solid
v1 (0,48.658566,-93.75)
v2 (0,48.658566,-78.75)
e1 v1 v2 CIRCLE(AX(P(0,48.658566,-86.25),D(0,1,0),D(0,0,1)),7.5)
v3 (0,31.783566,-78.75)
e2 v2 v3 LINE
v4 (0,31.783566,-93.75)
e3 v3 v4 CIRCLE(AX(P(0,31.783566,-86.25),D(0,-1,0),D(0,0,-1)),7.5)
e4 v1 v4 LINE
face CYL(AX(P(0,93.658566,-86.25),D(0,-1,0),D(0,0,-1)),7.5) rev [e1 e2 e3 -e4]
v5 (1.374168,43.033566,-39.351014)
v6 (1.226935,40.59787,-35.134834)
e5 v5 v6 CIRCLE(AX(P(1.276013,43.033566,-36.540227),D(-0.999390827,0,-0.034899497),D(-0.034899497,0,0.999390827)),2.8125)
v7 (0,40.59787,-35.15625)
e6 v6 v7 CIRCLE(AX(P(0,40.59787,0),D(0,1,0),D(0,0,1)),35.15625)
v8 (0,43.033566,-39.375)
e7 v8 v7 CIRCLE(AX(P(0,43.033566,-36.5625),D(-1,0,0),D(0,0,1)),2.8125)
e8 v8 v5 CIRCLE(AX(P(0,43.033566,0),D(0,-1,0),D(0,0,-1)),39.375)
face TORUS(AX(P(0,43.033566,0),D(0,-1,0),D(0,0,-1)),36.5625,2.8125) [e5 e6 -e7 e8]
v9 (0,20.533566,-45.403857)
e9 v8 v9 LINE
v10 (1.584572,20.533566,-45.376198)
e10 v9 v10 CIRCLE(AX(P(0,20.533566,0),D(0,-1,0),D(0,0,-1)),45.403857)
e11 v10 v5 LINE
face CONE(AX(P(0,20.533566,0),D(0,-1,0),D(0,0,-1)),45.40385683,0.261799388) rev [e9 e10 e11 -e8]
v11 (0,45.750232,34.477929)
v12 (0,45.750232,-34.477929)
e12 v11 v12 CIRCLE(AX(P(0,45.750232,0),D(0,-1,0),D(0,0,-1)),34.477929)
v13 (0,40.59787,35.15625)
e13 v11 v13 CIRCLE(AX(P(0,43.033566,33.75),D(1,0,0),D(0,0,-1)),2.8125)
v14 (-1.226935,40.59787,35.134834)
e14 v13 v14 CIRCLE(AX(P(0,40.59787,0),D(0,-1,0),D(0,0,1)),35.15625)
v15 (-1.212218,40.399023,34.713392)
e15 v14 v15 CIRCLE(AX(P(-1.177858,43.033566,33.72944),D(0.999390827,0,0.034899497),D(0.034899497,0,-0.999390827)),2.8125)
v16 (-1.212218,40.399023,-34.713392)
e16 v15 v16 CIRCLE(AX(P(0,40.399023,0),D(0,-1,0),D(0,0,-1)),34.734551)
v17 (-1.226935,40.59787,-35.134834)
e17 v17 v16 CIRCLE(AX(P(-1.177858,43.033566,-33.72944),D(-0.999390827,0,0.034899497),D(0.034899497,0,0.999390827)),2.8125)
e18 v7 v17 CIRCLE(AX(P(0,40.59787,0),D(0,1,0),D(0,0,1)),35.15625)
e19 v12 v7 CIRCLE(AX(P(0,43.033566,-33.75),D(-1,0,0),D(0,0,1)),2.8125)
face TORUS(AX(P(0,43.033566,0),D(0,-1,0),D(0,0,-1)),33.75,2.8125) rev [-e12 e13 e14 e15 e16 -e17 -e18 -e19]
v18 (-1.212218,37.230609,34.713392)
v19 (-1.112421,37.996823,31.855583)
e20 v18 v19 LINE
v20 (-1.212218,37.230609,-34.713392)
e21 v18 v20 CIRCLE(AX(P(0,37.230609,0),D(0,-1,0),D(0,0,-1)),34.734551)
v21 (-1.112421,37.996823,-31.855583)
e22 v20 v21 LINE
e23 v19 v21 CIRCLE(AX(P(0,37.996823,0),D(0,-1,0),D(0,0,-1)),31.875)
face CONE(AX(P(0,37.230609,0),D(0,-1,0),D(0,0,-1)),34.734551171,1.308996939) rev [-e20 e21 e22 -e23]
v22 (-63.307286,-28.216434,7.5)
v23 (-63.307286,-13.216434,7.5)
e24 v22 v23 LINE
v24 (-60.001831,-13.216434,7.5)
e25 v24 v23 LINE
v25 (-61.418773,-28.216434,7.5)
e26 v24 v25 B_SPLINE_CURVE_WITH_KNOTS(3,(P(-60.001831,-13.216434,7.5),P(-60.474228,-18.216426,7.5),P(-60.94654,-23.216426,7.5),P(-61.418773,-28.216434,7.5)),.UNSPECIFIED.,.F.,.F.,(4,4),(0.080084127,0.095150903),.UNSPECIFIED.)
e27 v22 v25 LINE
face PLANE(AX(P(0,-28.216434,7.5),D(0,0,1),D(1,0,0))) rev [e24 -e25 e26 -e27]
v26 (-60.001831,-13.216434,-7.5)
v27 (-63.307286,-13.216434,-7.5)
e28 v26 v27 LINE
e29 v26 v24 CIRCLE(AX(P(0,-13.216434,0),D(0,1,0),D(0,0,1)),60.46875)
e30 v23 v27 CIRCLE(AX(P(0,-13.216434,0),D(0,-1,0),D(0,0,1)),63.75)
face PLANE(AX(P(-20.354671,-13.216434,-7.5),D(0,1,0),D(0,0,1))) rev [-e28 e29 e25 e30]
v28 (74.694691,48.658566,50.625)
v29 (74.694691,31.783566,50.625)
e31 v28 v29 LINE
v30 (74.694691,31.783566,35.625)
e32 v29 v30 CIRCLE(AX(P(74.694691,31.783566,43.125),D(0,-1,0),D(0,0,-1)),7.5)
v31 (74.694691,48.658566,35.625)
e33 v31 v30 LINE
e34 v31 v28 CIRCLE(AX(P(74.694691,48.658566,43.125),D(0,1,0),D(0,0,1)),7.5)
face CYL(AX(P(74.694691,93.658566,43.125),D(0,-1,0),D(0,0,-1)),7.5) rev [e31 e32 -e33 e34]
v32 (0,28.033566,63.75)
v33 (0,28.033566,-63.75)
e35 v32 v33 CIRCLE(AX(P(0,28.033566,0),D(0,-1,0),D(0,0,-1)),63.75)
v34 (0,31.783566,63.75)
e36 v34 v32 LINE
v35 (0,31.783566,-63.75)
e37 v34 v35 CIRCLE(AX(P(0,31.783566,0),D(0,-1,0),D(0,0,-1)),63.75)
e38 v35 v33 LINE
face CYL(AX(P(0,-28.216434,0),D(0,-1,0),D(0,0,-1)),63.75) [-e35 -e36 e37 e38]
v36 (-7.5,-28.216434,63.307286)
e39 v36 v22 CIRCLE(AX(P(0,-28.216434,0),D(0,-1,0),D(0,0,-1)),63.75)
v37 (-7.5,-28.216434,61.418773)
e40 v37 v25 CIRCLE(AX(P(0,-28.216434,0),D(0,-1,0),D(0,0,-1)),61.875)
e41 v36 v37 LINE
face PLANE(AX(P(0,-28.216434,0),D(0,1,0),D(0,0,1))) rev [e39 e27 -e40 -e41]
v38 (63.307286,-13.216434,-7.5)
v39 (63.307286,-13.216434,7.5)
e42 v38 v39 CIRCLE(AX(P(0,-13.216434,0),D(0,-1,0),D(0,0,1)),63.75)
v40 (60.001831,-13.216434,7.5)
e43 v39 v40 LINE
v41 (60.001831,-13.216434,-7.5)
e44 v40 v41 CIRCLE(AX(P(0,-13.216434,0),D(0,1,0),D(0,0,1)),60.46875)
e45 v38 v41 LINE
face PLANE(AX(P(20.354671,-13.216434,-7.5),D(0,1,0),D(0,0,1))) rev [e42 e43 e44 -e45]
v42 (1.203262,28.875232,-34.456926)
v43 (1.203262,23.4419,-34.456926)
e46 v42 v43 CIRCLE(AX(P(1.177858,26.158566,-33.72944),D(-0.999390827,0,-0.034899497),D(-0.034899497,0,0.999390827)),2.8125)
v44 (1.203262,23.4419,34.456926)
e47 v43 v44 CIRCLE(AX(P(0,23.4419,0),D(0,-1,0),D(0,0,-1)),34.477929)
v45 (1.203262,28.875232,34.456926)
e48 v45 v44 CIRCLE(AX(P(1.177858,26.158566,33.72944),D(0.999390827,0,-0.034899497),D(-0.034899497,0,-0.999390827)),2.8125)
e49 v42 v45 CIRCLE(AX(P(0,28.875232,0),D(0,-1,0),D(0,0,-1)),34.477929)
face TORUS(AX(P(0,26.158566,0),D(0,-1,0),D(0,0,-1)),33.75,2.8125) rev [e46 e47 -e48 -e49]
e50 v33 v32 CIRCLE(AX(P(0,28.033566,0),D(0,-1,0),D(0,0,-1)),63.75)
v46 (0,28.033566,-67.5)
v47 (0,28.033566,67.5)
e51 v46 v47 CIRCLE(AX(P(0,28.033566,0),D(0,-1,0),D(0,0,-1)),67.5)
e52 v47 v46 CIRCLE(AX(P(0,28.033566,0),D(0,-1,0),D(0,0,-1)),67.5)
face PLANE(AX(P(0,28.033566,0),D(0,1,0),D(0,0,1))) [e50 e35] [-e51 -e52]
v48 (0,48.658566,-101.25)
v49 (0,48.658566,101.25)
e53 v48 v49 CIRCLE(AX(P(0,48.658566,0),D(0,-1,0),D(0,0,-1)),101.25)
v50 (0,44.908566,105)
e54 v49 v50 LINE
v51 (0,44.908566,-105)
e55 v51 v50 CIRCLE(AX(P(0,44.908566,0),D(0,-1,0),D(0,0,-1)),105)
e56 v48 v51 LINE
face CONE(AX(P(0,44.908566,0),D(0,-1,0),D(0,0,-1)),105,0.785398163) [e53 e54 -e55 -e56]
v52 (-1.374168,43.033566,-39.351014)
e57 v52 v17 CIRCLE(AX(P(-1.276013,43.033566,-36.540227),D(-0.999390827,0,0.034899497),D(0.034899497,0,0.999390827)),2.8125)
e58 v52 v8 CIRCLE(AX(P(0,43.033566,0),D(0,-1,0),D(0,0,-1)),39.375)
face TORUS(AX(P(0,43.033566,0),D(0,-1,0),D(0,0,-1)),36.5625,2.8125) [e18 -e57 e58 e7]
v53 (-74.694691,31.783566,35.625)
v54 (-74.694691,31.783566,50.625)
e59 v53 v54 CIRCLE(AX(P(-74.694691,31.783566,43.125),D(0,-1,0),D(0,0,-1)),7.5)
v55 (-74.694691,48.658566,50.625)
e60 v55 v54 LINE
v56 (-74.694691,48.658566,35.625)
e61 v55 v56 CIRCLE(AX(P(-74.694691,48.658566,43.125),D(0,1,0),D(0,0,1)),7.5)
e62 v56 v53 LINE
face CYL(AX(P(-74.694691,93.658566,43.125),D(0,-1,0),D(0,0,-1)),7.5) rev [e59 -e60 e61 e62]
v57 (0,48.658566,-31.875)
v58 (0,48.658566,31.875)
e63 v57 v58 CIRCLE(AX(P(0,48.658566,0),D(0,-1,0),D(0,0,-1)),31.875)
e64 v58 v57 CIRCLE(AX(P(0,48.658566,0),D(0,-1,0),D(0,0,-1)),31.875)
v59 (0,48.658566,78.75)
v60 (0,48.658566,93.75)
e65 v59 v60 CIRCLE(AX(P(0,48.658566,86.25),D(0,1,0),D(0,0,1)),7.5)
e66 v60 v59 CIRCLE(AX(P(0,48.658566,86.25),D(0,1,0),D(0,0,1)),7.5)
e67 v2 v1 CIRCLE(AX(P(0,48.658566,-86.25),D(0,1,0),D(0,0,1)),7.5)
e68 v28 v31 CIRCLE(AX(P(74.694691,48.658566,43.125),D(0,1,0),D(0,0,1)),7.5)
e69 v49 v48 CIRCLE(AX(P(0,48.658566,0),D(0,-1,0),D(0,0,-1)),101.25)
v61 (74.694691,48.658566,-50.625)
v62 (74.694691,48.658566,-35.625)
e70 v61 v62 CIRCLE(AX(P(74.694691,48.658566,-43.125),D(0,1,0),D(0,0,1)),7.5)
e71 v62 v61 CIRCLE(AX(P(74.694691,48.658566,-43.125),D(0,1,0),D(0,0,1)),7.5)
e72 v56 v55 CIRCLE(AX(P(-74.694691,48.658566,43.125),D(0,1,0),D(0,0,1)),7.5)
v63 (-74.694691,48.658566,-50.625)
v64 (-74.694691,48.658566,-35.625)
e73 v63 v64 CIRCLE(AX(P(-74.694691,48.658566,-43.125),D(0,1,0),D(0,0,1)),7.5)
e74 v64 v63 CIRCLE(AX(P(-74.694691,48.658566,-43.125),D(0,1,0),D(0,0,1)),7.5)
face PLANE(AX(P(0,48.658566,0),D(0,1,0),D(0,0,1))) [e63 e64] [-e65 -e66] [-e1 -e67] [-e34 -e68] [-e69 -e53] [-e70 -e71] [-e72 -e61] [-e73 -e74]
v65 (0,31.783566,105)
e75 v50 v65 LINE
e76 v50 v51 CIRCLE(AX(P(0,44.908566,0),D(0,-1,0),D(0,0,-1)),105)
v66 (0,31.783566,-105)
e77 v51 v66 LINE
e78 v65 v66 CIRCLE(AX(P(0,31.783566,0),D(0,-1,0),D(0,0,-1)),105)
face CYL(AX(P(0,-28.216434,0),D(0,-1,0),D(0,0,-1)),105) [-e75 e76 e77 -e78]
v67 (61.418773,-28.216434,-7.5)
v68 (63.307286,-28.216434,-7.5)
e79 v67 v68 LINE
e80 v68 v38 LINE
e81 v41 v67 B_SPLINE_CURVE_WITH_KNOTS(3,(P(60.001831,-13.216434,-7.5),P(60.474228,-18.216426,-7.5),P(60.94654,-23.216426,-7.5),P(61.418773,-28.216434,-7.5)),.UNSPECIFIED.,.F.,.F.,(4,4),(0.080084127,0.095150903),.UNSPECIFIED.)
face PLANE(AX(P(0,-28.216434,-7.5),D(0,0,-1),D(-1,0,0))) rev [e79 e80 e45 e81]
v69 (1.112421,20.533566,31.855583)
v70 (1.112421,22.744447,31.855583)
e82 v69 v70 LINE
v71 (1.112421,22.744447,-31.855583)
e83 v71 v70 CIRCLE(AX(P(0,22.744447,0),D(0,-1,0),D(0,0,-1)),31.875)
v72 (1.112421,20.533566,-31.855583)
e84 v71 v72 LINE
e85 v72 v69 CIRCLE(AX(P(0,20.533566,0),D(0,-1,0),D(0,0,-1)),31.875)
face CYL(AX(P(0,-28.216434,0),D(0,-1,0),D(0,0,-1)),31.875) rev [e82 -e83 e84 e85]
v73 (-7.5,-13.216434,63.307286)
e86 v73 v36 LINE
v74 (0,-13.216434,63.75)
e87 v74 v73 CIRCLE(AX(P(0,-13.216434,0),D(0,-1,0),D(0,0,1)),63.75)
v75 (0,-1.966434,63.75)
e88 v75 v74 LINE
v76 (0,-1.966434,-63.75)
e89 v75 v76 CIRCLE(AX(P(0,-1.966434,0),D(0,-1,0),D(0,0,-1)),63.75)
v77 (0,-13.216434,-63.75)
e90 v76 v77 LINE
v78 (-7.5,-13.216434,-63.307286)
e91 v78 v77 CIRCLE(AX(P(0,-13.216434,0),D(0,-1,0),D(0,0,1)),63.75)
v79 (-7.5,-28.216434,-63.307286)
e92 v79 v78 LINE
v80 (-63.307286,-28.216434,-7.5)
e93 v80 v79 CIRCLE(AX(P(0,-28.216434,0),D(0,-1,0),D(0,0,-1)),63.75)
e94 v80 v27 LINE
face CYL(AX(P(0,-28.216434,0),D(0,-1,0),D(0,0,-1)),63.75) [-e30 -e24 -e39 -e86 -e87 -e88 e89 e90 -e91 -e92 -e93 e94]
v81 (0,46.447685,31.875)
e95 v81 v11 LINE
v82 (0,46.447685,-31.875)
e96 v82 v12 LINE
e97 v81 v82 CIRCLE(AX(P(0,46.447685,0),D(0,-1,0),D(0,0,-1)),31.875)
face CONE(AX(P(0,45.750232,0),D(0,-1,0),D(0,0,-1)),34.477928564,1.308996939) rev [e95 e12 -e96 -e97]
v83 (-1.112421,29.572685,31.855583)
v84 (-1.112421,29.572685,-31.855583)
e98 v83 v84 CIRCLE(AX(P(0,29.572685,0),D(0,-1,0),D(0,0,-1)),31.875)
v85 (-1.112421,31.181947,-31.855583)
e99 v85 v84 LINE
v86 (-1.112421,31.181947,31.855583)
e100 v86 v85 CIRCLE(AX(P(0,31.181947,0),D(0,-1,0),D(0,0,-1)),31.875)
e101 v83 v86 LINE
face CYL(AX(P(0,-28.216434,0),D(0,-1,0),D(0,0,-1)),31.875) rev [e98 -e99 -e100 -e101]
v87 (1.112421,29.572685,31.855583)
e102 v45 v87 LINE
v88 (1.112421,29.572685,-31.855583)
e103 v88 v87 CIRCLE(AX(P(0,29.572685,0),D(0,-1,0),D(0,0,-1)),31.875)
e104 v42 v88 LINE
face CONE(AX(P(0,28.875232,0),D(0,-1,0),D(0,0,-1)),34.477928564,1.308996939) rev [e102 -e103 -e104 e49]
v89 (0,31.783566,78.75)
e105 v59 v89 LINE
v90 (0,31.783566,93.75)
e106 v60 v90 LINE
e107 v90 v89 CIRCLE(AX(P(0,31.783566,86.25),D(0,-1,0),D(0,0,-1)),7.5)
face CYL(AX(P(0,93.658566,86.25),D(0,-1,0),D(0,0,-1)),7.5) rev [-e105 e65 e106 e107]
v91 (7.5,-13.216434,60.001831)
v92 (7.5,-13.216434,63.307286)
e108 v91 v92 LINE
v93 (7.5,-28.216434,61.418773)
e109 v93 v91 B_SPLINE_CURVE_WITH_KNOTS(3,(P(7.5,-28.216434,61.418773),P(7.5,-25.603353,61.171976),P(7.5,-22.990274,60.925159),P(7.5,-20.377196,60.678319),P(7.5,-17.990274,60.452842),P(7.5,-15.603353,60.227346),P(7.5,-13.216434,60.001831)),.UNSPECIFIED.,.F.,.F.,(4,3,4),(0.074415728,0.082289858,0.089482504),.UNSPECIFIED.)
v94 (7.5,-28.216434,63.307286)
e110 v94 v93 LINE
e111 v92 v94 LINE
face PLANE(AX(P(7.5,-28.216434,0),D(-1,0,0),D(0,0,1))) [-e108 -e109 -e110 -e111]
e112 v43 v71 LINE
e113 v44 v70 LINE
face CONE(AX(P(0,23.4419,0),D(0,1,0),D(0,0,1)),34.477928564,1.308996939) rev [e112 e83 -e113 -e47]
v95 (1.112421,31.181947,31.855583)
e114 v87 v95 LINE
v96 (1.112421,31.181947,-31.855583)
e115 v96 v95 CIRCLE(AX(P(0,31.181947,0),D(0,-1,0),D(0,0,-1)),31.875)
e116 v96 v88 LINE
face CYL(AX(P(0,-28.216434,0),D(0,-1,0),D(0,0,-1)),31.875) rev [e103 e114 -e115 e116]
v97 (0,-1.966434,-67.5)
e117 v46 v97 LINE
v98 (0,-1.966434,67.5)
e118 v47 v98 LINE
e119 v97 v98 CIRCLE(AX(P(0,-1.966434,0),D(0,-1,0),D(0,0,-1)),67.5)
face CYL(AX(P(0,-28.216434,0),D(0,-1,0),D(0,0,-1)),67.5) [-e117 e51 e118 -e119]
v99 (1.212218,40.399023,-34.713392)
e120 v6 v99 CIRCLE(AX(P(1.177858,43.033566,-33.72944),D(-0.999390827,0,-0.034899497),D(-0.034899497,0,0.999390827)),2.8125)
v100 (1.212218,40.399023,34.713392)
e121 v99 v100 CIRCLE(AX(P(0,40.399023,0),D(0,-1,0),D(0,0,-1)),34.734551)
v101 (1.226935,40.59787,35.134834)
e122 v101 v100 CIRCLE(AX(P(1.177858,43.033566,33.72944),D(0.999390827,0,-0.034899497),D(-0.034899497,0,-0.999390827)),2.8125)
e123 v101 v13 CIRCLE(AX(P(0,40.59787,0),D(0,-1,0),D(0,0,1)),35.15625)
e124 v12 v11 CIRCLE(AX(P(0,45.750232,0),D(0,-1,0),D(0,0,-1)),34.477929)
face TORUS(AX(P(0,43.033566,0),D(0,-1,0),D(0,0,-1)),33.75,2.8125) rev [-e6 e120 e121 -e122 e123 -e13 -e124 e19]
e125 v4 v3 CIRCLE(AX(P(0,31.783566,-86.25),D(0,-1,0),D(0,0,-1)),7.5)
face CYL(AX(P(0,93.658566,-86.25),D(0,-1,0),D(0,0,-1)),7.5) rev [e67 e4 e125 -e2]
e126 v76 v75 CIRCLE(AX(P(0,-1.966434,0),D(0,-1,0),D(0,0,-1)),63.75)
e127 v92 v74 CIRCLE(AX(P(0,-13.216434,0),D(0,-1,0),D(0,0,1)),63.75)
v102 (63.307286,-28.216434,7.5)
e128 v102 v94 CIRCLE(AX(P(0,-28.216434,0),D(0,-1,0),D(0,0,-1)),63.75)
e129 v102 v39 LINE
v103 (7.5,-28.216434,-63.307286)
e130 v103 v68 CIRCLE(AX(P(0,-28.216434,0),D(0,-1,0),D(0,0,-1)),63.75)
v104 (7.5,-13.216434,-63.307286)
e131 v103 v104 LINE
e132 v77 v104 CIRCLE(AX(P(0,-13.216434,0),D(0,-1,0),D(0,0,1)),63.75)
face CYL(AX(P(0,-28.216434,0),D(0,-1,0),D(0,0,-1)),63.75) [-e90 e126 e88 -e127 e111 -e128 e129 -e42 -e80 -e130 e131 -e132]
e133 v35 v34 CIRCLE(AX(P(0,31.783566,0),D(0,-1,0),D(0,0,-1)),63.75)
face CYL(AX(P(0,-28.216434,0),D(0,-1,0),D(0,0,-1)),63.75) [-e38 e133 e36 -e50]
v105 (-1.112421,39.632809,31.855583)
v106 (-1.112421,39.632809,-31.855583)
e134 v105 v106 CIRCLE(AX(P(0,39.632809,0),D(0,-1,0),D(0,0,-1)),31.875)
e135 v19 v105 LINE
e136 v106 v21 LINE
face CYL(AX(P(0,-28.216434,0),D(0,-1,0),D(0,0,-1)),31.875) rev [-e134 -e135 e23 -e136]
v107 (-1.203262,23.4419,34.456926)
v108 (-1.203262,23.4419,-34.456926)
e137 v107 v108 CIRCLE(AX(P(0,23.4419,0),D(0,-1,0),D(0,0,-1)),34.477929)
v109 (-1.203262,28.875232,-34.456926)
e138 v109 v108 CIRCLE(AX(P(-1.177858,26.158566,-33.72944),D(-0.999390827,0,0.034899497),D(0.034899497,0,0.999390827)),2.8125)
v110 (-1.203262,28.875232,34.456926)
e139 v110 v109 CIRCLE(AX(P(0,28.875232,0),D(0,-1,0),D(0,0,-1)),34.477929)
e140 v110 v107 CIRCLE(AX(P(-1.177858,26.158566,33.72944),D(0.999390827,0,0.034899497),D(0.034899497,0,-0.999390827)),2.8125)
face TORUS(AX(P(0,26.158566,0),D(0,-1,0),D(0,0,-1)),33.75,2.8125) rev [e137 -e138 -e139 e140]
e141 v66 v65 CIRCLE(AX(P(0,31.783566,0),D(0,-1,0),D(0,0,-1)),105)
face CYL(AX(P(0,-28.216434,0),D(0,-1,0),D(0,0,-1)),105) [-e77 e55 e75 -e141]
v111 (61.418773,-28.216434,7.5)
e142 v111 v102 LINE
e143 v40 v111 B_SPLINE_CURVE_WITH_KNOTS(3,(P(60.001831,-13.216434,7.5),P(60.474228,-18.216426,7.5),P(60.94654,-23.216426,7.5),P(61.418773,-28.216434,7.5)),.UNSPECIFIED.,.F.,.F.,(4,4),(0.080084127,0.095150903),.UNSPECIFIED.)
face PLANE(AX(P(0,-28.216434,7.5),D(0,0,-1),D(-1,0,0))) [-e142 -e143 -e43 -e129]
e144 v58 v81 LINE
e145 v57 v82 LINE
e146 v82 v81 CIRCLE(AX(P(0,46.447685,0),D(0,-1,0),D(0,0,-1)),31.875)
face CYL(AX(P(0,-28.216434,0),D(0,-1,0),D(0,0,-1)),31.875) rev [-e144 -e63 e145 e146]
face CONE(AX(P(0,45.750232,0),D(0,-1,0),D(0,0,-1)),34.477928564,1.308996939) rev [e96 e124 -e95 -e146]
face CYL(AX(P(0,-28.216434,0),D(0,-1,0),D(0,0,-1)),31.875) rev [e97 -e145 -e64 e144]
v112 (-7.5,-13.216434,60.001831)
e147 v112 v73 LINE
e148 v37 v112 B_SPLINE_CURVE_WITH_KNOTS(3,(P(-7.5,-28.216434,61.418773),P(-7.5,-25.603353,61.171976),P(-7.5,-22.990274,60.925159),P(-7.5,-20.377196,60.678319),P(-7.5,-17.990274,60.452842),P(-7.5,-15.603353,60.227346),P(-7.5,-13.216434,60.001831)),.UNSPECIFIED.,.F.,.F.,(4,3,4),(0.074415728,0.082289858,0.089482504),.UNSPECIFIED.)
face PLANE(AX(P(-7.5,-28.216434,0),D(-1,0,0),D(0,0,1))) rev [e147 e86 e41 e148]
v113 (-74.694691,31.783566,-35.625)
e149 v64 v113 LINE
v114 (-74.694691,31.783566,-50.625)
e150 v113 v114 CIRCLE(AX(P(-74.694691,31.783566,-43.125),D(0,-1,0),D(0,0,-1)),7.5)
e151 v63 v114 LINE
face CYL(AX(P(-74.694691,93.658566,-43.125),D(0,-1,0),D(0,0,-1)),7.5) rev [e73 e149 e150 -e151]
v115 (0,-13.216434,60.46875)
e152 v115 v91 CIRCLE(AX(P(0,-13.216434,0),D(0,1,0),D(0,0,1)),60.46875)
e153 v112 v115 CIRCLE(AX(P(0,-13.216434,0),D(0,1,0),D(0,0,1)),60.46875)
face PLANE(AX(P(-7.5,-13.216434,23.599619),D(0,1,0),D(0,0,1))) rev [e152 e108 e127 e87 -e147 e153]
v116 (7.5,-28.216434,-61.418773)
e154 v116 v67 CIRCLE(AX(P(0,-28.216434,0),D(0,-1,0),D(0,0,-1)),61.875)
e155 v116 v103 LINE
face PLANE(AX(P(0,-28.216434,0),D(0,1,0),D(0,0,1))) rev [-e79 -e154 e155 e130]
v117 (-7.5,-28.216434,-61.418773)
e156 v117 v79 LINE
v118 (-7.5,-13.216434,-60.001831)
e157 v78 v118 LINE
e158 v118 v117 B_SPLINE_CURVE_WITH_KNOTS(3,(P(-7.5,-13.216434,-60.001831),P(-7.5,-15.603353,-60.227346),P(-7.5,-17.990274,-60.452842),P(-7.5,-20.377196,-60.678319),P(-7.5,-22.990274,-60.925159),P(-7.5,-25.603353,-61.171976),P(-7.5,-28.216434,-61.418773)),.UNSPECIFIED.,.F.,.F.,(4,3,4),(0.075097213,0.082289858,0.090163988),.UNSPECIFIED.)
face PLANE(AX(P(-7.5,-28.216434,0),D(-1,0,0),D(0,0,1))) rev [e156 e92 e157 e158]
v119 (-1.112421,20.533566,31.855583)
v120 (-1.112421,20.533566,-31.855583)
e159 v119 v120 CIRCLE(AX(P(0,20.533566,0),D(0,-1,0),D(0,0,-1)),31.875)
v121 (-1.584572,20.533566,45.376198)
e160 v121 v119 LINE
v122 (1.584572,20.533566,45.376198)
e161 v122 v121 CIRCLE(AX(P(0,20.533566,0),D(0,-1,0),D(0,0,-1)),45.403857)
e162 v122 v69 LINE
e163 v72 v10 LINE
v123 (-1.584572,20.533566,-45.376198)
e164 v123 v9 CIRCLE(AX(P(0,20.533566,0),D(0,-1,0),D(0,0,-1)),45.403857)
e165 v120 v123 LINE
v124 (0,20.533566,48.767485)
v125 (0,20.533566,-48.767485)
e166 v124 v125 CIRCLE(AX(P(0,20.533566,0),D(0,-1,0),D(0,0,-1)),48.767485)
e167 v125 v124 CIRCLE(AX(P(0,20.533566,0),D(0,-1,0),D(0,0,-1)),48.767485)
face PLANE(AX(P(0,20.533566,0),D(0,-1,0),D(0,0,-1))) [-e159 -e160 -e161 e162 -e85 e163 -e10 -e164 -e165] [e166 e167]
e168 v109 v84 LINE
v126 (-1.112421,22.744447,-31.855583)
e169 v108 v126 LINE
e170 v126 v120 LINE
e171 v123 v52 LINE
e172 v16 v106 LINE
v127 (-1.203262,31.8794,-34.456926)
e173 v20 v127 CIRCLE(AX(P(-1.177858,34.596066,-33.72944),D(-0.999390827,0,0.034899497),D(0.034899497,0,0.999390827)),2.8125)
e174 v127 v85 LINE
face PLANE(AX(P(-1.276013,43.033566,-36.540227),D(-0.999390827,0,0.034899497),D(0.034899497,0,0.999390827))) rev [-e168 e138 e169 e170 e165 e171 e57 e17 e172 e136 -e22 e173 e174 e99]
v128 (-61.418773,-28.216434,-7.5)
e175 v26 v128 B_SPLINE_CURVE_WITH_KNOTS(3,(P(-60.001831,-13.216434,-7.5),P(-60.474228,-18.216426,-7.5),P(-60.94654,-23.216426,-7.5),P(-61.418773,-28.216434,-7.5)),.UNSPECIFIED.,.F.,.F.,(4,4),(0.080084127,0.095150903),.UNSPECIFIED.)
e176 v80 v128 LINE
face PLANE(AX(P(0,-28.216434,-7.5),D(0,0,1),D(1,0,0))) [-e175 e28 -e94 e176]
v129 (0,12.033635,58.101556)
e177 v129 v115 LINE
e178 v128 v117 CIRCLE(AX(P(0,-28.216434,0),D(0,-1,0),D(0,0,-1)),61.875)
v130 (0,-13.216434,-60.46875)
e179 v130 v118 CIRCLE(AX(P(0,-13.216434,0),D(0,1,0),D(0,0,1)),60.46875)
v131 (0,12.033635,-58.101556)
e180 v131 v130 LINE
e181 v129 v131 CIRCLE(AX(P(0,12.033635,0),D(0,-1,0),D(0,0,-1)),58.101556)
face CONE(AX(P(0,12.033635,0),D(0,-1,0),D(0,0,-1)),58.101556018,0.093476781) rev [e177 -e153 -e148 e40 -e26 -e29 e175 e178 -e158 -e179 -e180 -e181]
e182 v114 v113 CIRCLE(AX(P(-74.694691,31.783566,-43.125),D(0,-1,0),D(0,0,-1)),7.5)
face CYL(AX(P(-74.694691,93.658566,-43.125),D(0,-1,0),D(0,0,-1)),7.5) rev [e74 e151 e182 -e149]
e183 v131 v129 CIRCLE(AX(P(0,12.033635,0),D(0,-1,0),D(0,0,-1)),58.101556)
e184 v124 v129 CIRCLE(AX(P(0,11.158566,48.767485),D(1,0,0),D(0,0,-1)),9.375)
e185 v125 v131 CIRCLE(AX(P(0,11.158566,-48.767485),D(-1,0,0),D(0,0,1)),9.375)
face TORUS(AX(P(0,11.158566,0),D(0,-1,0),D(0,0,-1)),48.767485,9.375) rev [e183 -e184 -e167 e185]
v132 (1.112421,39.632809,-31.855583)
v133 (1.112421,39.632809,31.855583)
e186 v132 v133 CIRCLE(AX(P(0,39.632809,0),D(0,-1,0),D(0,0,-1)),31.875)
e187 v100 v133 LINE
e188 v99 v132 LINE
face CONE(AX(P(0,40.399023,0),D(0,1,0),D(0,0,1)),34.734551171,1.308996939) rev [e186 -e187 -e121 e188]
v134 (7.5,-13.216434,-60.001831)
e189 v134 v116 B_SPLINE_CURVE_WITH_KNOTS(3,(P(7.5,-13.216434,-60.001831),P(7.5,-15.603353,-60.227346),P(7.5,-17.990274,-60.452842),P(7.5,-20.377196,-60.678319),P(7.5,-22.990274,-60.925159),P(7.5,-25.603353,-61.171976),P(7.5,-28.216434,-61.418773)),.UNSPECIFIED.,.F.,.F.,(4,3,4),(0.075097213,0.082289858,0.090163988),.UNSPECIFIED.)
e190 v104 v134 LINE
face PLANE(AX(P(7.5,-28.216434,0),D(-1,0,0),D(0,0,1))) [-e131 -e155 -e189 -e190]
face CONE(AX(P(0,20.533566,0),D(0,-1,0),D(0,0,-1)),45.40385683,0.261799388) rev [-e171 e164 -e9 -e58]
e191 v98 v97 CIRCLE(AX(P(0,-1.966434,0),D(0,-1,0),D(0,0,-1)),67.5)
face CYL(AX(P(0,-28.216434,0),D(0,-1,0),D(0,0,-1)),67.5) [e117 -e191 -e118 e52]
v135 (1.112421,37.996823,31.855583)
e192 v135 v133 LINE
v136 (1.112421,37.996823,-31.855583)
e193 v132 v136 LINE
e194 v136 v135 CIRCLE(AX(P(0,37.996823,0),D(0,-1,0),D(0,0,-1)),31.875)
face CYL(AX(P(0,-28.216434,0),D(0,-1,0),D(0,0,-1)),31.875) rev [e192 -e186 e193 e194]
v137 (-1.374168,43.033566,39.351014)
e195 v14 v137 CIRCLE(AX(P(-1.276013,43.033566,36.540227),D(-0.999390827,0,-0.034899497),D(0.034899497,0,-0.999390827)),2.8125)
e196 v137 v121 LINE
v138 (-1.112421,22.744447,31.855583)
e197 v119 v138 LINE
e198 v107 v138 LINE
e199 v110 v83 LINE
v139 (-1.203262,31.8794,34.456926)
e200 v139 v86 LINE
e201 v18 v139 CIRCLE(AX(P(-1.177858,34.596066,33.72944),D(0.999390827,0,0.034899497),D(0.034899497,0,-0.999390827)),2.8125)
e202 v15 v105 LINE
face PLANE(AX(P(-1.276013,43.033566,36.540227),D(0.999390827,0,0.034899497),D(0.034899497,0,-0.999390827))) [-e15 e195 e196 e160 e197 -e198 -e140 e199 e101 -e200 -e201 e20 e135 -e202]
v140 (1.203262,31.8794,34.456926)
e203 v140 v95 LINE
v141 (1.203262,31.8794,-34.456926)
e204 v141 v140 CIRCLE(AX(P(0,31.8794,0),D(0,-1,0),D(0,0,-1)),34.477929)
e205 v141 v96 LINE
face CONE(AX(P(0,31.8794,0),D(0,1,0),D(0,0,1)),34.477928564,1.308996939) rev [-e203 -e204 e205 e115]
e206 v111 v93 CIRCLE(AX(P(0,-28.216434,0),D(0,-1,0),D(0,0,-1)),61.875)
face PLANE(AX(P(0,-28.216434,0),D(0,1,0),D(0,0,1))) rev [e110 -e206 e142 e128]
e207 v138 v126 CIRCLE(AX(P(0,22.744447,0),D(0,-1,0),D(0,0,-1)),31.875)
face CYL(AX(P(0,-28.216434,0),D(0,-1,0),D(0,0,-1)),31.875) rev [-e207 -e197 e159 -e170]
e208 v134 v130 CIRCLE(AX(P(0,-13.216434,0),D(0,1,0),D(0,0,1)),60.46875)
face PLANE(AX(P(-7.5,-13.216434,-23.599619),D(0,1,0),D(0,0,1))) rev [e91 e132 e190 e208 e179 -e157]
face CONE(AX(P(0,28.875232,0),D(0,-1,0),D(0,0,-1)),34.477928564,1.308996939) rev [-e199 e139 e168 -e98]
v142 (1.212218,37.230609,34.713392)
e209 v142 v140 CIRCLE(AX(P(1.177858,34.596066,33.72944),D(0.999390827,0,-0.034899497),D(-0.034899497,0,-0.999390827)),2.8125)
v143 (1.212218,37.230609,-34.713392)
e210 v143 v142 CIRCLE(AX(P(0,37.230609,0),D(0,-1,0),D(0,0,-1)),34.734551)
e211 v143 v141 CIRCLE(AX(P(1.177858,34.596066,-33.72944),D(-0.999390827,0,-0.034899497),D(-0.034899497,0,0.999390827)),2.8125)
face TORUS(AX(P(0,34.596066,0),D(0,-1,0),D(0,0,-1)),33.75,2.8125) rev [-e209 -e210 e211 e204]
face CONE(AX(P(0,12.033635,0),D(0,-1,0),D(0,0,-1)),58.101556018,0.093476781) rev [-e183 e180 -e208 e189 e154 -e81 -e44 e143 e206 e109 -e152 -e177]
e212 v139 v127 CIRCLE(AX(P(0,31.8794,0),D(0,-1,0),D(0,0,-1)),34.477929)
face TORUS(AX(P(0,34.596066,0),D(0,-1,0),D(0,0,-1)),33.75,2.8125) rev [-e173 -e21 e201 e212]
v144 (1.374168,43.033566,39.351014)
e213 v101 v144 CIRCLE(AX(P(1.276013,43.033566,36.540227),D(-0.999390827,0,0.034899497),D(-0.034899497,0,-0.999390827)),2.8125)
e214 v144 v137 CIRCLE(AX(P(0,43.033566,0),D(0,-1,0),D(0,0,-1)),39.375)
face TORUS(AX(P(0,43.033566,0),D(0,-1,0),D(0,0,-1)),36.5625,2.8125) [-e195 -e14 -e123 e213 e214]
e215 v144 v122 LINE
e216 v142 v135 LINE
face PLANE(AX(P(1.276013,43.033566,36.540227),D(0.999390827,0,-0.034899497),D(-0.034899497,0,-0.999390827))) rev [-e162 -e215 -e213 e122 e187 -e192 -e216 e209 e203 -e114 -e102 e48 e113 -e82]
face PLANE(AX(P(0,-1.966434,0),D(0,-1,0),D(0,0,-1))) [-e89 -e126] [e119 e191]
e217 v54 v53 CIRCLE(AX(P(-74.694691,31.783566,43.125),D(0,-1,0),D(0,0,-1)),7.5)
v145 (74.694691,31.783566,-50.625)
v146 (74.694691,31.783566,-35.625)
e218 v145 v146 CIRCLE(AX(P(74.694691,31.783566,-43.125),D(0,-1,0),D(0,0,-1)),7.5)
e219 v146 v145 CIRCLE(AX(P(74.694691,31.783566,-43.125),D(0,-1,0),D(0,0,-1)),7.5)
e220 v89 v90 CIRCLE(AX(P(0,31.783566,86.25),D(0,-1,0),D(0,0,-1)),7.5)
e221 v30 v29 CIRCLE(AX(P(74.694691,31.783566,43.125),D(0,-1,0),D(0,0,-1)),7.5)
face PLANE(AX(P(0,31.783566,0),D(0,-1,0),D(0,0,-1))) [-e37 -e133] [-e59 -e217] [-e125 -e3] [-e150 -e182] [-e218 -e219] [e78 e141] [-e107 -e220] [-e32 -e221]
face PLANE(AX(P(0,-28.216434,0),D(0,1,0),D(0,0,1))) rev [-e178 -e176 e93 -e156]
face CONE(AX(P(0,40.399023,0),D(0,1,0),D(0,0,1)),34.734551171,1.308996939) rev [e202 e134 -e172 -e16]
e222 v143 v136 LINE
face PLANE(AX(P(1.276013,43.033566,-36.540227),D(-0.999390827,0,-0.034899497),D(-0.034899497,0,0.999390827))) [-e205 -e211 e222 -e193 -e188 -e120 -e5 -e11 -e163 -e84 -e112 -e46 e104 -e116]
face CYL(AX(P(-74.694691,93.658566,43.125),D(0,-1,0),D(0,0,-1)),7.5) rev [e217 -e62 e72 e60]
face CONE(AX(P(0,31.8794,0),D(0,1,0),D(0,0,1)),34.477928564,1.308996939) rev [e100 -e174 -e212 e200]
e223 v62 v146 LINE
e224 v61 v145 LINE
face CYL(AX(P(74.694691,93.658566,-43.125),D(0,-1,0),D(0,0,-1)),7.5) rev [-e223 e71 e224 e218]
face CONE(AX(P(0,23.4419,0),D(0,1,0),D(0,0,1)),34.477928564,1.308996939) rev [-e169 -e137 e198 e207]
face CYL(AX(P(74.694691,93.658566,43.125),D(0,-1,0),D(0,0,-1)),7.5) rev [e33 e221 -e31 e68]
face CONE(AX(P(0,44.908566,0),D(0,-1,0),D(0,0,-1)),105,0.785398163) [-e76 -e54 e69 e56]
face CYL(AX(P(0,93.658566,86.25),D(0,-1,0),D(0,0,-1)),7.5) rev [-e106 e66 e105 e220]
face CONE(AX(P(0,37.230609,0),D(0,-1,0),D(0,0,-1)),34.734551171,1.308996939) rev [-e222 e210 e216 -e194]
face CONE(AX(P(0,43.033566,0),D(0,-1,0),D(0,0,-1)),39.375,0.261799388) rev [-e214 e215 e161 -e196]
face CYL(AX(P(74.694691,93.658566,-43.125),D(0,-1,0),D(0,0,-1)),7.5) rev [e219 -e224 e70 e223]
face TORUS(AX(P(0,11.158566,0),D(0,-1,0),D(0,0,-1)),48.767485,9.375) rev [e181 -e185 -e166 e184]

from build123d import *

# Parameters (mm, degrees)
CUT_REVOLVE1_ANGLE = 4.000000000000009
SKETCH4_W          = 37.759390331998226
SKETCH4_H          = 8
CUT_EXTRUDE1_DEPTH = 4
SKETCH5_W          = 44.9966068122979
SKETCH5_H          = 8
CUT_EXTRUDE2_DEPTH = 4
SKETCH6_R          = 4.000000000000005
SKETCH6_R_2        = 4.000000000000001
SKETCH6_R_3        = 3.999999999999999
CUT_EXTRUDE3_DEPTH = 65
SCALE_1_SCALE      = 1.875


with BuildPart() as part:
    # Sketch1 → Revolve1 (revolve)
    with BuildSketch(Plane.XY, mode=Mode.PRIVATE) as revolve1_sk:
        with BuildLine():
            Line((-34, 13.999999999999998), (-34, 0))
            Line((-34, 0), (-33, 0))
            Line((-33, 0), (-30.987496542800134, 21.466703543465286))
            ThreePointArc((-30.987496542800134, 21.466703543465286), (-29.37581336604471, 24.696857971124018), (-26.009325412503696, 25.999999999999996))
            Line((-26.009325412503696, 25.999999999999996), (-17, 25.999999999999996))
            Line((-17, 25.999999999999996), (-17.000000000000004, 27.17913653695376))
            Line((-17.000000000000004, 27.17913653695376), (-18.388228567653776, 27.551111260566394))
            ThreePointArc((-18.388228567653776, 27.551111260566394), (-19.500000000000014, 28.999999999999986), (-18.3882285676538, 30.448888739433595))
            Line((-18.3882285676538, 30.448888739433595), (-17.000000000000007, 30.820863463046255))
            Line((-17.000000000000007, 30.820863463046255), (-17.000000000000007, 31.679136536953756))
            Line((-17.000000000000007, 31.679136536953756), (-18.38822856765378, 32.05111126056639))
            ThreePointArc((-18.38822856765378, 32.05111126056638), (-19.49827813558921, 33.42814856706124), (-18.52509395794485, 34.90508944033103))
            Line((-18.525093957944854, 34.90508944033104), (-17.000000000000007, 35.31373713474397))
            Line((-17.000000000000007, 35.31373713474397), (-17.000000000000007, 36.179136536953735))
            Line((-17.000000000000007, 36.179136536953735), (-17.000000000000004, 36.18626286525602))
            Line((-17.000000000000004, 36.18626286525602), (-18.525093957944854, 36.59491055966894))
            ThreePointArc((-18.525093957944854, 36.59491055966894), (-19.49827813558921, 38.07185143293873), (-18.38822856765378, 39.44888873943359))
            Line((-18.38822856765378, 39.44888873943359), (-17.000000000000007, 39.82086346304622))
            Line((-17.000000000000007, 39.82086346304622), (-17, 40.99999999999999))
            Line((-17, 40.99999999999999), (-54, 40.99999999999999))
            Line((-54, 40.99999999999999), (-56, 39))
            Line((-56, 39), (-56, 32))
            Line((-56, 32), (-34, 31.999999999999993))
            Line((-34, 31.999999999999993), (-34, 29.999999999999993))
            Line((-34, 29.999999999999993), (-36.00000000000001, 29.999999999999993))
            Line((-36.00000000000001, 29.999999999999993), (-36.00000000000001, 13.999999999999998))
            Line((-36.00000000000001, 13.999999999999998), (-34, 13.999999999999998))
        make_face()
    revolve(revolve1_sk.sketch.rotate(Axis((0, 0, 0), (0, 1, 0)), 270), axis=Axis((0, 0, 0), (0, 1, 0)))

    # Sketch3 → Cut-Revolve1 (revolve, symmetric, cut)
    with BuildSketch(Plane(origin=(0, 0, 0), x_dir=(0, 0, -1), z_dir=(1, 0, 0))) as cut_revolve1_sk:
        with BuildLine():
            Line((-17.000000000000014, 32.71643849545569), (-17.000000000000014, 25.999999999999996))
            Line((-17.000000000000014, 25.999999999999996), (-24.215390309173507, 25.999999999999996))
            Line((-24.215390309173507, 25.999999999999996), (-21.000000000000025, 37.99999999999999))
            ThreePointArc((-21.000000000000025, 37.99999999999999), (-19.500000000000025, 36.49999999999999), (-18.00000000000002, 37.99999999999999))
            Line((-18.00000000000002, 37.99999999999999), (-17.000000000000014, 37.99999999999999))
            Line((-17.000000000000014, 37.99999999999999), (-17.000000000000014, 32.71643849545569))
        make_face()
        with BuildLine():
            Line((18.00000000000002, 37.99999999999999), (17.000000000000014, 37.99999999999999))
            Line((17.000000000000014, 37.99999999999999), (17.000000000000014, 32.71643849545569))
            Line((17.000000000000014, 32.71643849545569), (17.000000000000014, 25.999999999999996))
            Line((17.000000000000014, 25.999999999999996), (24.215390309173507, 25.999999999999996))
            Line((24.215390309173507, 25.999999999999996), (21.000000000000025, 37.99999999999999))
            ThreePointArc((21.000000000000025, 37.99999999999999), (19.500000000000025, 36.49999999999999), (18.00000000000002, 37.99999999999999))
        make_face()
    revolve(axis=Axis((0, 0, 0), (0, 1, 0)), revolution_arc=CUT_REVOLVE1_ANGLE / 2, mode=Mode.SUBTRACT)
    revolve(cut_revolve1_sk.sketch, axis=Axis((0, 0, 0), (0, -1, 0)), revolution_arc=CUT_REVOLVE1_ANGLE / 2, mode=Mode.SUBTRACT)

    # Sketch4 → Cut-Extrude1 (cut, symmetric)
    with BuildSketch(Plane(origin=(0, 0, 0), x_dir=(0, 0, -1), z_dir=(1, 0, 0))):
        with Locations((31.466158609998526, 4)):
            Rectangle(SKETCH4_W, SKETCH4_H)
        with Locations((-31.466158609998526, 4)):
            Rectangle(SKETCH4_W, SKETCH4_H)
    extrude(amount=CUT_EXTRUDE1_DEPTH, both=True, mode=Mode.SUBTRACT)

    # Sketch5 → Cut-Extrude2 (cut, symmetric)
    with BuildSketch(Plane.XY):
        with Locations((33.35412812659844, 4)):
            Rectangle(SKETCH5_W, SKETCH5_H)
        with Locations((-33.35412812659844, 4)):
            Rectangle(SKETCH5_W, SKETCH5_H)
    extrude(amount=CUT_EXTRUDE2_DEPTH, both=True, mode=Mode.SUBTRACT)

    # Sketch6 → Cut-Extrude3 (cut)
    with BuildSketch(Plane.XZ):
        with Locations(Location((-39.837168574084245, -22.9999999999999, 0), (0, 0, 270))):
            Circle(SKETCH6_R)
        with Locations(Location((0, 46, 0), (0, 0, 270))):
            Circle(SKETCH6_R_2)
        with Locations(Location((39.837168574084224, 22.999999999999908, 0), (0, 0, 270))):
            Circle(SKETCH6_R_3)
        with Locations(Location((-39.837168574084245, 22.9999999999999, 0), (0, 0, 270))):
            Circle(SKETCH6_R)
        with Locations(Location((0, -46, 0), (0, 0, 270))):
            Circle(SKETCH6_R_2)
        with Locations(Location((39.837168574084224, -22.999999999999908, 0), (0, 0, 270))):
            Circle(SKETCH6_R_3)
    extrude(amount=-CUT_EXTRUDE3_DEPTH, mode=Mode.SUBTRACT)


with BuildPart() as part_1:
    # Scale 1: scaled about (0, 32.2473532, 0)
    add(part.part.scale(SCALE_1_SCALE).moved(Location((0, -28.21643405, 0))))


solid = part_1.part
